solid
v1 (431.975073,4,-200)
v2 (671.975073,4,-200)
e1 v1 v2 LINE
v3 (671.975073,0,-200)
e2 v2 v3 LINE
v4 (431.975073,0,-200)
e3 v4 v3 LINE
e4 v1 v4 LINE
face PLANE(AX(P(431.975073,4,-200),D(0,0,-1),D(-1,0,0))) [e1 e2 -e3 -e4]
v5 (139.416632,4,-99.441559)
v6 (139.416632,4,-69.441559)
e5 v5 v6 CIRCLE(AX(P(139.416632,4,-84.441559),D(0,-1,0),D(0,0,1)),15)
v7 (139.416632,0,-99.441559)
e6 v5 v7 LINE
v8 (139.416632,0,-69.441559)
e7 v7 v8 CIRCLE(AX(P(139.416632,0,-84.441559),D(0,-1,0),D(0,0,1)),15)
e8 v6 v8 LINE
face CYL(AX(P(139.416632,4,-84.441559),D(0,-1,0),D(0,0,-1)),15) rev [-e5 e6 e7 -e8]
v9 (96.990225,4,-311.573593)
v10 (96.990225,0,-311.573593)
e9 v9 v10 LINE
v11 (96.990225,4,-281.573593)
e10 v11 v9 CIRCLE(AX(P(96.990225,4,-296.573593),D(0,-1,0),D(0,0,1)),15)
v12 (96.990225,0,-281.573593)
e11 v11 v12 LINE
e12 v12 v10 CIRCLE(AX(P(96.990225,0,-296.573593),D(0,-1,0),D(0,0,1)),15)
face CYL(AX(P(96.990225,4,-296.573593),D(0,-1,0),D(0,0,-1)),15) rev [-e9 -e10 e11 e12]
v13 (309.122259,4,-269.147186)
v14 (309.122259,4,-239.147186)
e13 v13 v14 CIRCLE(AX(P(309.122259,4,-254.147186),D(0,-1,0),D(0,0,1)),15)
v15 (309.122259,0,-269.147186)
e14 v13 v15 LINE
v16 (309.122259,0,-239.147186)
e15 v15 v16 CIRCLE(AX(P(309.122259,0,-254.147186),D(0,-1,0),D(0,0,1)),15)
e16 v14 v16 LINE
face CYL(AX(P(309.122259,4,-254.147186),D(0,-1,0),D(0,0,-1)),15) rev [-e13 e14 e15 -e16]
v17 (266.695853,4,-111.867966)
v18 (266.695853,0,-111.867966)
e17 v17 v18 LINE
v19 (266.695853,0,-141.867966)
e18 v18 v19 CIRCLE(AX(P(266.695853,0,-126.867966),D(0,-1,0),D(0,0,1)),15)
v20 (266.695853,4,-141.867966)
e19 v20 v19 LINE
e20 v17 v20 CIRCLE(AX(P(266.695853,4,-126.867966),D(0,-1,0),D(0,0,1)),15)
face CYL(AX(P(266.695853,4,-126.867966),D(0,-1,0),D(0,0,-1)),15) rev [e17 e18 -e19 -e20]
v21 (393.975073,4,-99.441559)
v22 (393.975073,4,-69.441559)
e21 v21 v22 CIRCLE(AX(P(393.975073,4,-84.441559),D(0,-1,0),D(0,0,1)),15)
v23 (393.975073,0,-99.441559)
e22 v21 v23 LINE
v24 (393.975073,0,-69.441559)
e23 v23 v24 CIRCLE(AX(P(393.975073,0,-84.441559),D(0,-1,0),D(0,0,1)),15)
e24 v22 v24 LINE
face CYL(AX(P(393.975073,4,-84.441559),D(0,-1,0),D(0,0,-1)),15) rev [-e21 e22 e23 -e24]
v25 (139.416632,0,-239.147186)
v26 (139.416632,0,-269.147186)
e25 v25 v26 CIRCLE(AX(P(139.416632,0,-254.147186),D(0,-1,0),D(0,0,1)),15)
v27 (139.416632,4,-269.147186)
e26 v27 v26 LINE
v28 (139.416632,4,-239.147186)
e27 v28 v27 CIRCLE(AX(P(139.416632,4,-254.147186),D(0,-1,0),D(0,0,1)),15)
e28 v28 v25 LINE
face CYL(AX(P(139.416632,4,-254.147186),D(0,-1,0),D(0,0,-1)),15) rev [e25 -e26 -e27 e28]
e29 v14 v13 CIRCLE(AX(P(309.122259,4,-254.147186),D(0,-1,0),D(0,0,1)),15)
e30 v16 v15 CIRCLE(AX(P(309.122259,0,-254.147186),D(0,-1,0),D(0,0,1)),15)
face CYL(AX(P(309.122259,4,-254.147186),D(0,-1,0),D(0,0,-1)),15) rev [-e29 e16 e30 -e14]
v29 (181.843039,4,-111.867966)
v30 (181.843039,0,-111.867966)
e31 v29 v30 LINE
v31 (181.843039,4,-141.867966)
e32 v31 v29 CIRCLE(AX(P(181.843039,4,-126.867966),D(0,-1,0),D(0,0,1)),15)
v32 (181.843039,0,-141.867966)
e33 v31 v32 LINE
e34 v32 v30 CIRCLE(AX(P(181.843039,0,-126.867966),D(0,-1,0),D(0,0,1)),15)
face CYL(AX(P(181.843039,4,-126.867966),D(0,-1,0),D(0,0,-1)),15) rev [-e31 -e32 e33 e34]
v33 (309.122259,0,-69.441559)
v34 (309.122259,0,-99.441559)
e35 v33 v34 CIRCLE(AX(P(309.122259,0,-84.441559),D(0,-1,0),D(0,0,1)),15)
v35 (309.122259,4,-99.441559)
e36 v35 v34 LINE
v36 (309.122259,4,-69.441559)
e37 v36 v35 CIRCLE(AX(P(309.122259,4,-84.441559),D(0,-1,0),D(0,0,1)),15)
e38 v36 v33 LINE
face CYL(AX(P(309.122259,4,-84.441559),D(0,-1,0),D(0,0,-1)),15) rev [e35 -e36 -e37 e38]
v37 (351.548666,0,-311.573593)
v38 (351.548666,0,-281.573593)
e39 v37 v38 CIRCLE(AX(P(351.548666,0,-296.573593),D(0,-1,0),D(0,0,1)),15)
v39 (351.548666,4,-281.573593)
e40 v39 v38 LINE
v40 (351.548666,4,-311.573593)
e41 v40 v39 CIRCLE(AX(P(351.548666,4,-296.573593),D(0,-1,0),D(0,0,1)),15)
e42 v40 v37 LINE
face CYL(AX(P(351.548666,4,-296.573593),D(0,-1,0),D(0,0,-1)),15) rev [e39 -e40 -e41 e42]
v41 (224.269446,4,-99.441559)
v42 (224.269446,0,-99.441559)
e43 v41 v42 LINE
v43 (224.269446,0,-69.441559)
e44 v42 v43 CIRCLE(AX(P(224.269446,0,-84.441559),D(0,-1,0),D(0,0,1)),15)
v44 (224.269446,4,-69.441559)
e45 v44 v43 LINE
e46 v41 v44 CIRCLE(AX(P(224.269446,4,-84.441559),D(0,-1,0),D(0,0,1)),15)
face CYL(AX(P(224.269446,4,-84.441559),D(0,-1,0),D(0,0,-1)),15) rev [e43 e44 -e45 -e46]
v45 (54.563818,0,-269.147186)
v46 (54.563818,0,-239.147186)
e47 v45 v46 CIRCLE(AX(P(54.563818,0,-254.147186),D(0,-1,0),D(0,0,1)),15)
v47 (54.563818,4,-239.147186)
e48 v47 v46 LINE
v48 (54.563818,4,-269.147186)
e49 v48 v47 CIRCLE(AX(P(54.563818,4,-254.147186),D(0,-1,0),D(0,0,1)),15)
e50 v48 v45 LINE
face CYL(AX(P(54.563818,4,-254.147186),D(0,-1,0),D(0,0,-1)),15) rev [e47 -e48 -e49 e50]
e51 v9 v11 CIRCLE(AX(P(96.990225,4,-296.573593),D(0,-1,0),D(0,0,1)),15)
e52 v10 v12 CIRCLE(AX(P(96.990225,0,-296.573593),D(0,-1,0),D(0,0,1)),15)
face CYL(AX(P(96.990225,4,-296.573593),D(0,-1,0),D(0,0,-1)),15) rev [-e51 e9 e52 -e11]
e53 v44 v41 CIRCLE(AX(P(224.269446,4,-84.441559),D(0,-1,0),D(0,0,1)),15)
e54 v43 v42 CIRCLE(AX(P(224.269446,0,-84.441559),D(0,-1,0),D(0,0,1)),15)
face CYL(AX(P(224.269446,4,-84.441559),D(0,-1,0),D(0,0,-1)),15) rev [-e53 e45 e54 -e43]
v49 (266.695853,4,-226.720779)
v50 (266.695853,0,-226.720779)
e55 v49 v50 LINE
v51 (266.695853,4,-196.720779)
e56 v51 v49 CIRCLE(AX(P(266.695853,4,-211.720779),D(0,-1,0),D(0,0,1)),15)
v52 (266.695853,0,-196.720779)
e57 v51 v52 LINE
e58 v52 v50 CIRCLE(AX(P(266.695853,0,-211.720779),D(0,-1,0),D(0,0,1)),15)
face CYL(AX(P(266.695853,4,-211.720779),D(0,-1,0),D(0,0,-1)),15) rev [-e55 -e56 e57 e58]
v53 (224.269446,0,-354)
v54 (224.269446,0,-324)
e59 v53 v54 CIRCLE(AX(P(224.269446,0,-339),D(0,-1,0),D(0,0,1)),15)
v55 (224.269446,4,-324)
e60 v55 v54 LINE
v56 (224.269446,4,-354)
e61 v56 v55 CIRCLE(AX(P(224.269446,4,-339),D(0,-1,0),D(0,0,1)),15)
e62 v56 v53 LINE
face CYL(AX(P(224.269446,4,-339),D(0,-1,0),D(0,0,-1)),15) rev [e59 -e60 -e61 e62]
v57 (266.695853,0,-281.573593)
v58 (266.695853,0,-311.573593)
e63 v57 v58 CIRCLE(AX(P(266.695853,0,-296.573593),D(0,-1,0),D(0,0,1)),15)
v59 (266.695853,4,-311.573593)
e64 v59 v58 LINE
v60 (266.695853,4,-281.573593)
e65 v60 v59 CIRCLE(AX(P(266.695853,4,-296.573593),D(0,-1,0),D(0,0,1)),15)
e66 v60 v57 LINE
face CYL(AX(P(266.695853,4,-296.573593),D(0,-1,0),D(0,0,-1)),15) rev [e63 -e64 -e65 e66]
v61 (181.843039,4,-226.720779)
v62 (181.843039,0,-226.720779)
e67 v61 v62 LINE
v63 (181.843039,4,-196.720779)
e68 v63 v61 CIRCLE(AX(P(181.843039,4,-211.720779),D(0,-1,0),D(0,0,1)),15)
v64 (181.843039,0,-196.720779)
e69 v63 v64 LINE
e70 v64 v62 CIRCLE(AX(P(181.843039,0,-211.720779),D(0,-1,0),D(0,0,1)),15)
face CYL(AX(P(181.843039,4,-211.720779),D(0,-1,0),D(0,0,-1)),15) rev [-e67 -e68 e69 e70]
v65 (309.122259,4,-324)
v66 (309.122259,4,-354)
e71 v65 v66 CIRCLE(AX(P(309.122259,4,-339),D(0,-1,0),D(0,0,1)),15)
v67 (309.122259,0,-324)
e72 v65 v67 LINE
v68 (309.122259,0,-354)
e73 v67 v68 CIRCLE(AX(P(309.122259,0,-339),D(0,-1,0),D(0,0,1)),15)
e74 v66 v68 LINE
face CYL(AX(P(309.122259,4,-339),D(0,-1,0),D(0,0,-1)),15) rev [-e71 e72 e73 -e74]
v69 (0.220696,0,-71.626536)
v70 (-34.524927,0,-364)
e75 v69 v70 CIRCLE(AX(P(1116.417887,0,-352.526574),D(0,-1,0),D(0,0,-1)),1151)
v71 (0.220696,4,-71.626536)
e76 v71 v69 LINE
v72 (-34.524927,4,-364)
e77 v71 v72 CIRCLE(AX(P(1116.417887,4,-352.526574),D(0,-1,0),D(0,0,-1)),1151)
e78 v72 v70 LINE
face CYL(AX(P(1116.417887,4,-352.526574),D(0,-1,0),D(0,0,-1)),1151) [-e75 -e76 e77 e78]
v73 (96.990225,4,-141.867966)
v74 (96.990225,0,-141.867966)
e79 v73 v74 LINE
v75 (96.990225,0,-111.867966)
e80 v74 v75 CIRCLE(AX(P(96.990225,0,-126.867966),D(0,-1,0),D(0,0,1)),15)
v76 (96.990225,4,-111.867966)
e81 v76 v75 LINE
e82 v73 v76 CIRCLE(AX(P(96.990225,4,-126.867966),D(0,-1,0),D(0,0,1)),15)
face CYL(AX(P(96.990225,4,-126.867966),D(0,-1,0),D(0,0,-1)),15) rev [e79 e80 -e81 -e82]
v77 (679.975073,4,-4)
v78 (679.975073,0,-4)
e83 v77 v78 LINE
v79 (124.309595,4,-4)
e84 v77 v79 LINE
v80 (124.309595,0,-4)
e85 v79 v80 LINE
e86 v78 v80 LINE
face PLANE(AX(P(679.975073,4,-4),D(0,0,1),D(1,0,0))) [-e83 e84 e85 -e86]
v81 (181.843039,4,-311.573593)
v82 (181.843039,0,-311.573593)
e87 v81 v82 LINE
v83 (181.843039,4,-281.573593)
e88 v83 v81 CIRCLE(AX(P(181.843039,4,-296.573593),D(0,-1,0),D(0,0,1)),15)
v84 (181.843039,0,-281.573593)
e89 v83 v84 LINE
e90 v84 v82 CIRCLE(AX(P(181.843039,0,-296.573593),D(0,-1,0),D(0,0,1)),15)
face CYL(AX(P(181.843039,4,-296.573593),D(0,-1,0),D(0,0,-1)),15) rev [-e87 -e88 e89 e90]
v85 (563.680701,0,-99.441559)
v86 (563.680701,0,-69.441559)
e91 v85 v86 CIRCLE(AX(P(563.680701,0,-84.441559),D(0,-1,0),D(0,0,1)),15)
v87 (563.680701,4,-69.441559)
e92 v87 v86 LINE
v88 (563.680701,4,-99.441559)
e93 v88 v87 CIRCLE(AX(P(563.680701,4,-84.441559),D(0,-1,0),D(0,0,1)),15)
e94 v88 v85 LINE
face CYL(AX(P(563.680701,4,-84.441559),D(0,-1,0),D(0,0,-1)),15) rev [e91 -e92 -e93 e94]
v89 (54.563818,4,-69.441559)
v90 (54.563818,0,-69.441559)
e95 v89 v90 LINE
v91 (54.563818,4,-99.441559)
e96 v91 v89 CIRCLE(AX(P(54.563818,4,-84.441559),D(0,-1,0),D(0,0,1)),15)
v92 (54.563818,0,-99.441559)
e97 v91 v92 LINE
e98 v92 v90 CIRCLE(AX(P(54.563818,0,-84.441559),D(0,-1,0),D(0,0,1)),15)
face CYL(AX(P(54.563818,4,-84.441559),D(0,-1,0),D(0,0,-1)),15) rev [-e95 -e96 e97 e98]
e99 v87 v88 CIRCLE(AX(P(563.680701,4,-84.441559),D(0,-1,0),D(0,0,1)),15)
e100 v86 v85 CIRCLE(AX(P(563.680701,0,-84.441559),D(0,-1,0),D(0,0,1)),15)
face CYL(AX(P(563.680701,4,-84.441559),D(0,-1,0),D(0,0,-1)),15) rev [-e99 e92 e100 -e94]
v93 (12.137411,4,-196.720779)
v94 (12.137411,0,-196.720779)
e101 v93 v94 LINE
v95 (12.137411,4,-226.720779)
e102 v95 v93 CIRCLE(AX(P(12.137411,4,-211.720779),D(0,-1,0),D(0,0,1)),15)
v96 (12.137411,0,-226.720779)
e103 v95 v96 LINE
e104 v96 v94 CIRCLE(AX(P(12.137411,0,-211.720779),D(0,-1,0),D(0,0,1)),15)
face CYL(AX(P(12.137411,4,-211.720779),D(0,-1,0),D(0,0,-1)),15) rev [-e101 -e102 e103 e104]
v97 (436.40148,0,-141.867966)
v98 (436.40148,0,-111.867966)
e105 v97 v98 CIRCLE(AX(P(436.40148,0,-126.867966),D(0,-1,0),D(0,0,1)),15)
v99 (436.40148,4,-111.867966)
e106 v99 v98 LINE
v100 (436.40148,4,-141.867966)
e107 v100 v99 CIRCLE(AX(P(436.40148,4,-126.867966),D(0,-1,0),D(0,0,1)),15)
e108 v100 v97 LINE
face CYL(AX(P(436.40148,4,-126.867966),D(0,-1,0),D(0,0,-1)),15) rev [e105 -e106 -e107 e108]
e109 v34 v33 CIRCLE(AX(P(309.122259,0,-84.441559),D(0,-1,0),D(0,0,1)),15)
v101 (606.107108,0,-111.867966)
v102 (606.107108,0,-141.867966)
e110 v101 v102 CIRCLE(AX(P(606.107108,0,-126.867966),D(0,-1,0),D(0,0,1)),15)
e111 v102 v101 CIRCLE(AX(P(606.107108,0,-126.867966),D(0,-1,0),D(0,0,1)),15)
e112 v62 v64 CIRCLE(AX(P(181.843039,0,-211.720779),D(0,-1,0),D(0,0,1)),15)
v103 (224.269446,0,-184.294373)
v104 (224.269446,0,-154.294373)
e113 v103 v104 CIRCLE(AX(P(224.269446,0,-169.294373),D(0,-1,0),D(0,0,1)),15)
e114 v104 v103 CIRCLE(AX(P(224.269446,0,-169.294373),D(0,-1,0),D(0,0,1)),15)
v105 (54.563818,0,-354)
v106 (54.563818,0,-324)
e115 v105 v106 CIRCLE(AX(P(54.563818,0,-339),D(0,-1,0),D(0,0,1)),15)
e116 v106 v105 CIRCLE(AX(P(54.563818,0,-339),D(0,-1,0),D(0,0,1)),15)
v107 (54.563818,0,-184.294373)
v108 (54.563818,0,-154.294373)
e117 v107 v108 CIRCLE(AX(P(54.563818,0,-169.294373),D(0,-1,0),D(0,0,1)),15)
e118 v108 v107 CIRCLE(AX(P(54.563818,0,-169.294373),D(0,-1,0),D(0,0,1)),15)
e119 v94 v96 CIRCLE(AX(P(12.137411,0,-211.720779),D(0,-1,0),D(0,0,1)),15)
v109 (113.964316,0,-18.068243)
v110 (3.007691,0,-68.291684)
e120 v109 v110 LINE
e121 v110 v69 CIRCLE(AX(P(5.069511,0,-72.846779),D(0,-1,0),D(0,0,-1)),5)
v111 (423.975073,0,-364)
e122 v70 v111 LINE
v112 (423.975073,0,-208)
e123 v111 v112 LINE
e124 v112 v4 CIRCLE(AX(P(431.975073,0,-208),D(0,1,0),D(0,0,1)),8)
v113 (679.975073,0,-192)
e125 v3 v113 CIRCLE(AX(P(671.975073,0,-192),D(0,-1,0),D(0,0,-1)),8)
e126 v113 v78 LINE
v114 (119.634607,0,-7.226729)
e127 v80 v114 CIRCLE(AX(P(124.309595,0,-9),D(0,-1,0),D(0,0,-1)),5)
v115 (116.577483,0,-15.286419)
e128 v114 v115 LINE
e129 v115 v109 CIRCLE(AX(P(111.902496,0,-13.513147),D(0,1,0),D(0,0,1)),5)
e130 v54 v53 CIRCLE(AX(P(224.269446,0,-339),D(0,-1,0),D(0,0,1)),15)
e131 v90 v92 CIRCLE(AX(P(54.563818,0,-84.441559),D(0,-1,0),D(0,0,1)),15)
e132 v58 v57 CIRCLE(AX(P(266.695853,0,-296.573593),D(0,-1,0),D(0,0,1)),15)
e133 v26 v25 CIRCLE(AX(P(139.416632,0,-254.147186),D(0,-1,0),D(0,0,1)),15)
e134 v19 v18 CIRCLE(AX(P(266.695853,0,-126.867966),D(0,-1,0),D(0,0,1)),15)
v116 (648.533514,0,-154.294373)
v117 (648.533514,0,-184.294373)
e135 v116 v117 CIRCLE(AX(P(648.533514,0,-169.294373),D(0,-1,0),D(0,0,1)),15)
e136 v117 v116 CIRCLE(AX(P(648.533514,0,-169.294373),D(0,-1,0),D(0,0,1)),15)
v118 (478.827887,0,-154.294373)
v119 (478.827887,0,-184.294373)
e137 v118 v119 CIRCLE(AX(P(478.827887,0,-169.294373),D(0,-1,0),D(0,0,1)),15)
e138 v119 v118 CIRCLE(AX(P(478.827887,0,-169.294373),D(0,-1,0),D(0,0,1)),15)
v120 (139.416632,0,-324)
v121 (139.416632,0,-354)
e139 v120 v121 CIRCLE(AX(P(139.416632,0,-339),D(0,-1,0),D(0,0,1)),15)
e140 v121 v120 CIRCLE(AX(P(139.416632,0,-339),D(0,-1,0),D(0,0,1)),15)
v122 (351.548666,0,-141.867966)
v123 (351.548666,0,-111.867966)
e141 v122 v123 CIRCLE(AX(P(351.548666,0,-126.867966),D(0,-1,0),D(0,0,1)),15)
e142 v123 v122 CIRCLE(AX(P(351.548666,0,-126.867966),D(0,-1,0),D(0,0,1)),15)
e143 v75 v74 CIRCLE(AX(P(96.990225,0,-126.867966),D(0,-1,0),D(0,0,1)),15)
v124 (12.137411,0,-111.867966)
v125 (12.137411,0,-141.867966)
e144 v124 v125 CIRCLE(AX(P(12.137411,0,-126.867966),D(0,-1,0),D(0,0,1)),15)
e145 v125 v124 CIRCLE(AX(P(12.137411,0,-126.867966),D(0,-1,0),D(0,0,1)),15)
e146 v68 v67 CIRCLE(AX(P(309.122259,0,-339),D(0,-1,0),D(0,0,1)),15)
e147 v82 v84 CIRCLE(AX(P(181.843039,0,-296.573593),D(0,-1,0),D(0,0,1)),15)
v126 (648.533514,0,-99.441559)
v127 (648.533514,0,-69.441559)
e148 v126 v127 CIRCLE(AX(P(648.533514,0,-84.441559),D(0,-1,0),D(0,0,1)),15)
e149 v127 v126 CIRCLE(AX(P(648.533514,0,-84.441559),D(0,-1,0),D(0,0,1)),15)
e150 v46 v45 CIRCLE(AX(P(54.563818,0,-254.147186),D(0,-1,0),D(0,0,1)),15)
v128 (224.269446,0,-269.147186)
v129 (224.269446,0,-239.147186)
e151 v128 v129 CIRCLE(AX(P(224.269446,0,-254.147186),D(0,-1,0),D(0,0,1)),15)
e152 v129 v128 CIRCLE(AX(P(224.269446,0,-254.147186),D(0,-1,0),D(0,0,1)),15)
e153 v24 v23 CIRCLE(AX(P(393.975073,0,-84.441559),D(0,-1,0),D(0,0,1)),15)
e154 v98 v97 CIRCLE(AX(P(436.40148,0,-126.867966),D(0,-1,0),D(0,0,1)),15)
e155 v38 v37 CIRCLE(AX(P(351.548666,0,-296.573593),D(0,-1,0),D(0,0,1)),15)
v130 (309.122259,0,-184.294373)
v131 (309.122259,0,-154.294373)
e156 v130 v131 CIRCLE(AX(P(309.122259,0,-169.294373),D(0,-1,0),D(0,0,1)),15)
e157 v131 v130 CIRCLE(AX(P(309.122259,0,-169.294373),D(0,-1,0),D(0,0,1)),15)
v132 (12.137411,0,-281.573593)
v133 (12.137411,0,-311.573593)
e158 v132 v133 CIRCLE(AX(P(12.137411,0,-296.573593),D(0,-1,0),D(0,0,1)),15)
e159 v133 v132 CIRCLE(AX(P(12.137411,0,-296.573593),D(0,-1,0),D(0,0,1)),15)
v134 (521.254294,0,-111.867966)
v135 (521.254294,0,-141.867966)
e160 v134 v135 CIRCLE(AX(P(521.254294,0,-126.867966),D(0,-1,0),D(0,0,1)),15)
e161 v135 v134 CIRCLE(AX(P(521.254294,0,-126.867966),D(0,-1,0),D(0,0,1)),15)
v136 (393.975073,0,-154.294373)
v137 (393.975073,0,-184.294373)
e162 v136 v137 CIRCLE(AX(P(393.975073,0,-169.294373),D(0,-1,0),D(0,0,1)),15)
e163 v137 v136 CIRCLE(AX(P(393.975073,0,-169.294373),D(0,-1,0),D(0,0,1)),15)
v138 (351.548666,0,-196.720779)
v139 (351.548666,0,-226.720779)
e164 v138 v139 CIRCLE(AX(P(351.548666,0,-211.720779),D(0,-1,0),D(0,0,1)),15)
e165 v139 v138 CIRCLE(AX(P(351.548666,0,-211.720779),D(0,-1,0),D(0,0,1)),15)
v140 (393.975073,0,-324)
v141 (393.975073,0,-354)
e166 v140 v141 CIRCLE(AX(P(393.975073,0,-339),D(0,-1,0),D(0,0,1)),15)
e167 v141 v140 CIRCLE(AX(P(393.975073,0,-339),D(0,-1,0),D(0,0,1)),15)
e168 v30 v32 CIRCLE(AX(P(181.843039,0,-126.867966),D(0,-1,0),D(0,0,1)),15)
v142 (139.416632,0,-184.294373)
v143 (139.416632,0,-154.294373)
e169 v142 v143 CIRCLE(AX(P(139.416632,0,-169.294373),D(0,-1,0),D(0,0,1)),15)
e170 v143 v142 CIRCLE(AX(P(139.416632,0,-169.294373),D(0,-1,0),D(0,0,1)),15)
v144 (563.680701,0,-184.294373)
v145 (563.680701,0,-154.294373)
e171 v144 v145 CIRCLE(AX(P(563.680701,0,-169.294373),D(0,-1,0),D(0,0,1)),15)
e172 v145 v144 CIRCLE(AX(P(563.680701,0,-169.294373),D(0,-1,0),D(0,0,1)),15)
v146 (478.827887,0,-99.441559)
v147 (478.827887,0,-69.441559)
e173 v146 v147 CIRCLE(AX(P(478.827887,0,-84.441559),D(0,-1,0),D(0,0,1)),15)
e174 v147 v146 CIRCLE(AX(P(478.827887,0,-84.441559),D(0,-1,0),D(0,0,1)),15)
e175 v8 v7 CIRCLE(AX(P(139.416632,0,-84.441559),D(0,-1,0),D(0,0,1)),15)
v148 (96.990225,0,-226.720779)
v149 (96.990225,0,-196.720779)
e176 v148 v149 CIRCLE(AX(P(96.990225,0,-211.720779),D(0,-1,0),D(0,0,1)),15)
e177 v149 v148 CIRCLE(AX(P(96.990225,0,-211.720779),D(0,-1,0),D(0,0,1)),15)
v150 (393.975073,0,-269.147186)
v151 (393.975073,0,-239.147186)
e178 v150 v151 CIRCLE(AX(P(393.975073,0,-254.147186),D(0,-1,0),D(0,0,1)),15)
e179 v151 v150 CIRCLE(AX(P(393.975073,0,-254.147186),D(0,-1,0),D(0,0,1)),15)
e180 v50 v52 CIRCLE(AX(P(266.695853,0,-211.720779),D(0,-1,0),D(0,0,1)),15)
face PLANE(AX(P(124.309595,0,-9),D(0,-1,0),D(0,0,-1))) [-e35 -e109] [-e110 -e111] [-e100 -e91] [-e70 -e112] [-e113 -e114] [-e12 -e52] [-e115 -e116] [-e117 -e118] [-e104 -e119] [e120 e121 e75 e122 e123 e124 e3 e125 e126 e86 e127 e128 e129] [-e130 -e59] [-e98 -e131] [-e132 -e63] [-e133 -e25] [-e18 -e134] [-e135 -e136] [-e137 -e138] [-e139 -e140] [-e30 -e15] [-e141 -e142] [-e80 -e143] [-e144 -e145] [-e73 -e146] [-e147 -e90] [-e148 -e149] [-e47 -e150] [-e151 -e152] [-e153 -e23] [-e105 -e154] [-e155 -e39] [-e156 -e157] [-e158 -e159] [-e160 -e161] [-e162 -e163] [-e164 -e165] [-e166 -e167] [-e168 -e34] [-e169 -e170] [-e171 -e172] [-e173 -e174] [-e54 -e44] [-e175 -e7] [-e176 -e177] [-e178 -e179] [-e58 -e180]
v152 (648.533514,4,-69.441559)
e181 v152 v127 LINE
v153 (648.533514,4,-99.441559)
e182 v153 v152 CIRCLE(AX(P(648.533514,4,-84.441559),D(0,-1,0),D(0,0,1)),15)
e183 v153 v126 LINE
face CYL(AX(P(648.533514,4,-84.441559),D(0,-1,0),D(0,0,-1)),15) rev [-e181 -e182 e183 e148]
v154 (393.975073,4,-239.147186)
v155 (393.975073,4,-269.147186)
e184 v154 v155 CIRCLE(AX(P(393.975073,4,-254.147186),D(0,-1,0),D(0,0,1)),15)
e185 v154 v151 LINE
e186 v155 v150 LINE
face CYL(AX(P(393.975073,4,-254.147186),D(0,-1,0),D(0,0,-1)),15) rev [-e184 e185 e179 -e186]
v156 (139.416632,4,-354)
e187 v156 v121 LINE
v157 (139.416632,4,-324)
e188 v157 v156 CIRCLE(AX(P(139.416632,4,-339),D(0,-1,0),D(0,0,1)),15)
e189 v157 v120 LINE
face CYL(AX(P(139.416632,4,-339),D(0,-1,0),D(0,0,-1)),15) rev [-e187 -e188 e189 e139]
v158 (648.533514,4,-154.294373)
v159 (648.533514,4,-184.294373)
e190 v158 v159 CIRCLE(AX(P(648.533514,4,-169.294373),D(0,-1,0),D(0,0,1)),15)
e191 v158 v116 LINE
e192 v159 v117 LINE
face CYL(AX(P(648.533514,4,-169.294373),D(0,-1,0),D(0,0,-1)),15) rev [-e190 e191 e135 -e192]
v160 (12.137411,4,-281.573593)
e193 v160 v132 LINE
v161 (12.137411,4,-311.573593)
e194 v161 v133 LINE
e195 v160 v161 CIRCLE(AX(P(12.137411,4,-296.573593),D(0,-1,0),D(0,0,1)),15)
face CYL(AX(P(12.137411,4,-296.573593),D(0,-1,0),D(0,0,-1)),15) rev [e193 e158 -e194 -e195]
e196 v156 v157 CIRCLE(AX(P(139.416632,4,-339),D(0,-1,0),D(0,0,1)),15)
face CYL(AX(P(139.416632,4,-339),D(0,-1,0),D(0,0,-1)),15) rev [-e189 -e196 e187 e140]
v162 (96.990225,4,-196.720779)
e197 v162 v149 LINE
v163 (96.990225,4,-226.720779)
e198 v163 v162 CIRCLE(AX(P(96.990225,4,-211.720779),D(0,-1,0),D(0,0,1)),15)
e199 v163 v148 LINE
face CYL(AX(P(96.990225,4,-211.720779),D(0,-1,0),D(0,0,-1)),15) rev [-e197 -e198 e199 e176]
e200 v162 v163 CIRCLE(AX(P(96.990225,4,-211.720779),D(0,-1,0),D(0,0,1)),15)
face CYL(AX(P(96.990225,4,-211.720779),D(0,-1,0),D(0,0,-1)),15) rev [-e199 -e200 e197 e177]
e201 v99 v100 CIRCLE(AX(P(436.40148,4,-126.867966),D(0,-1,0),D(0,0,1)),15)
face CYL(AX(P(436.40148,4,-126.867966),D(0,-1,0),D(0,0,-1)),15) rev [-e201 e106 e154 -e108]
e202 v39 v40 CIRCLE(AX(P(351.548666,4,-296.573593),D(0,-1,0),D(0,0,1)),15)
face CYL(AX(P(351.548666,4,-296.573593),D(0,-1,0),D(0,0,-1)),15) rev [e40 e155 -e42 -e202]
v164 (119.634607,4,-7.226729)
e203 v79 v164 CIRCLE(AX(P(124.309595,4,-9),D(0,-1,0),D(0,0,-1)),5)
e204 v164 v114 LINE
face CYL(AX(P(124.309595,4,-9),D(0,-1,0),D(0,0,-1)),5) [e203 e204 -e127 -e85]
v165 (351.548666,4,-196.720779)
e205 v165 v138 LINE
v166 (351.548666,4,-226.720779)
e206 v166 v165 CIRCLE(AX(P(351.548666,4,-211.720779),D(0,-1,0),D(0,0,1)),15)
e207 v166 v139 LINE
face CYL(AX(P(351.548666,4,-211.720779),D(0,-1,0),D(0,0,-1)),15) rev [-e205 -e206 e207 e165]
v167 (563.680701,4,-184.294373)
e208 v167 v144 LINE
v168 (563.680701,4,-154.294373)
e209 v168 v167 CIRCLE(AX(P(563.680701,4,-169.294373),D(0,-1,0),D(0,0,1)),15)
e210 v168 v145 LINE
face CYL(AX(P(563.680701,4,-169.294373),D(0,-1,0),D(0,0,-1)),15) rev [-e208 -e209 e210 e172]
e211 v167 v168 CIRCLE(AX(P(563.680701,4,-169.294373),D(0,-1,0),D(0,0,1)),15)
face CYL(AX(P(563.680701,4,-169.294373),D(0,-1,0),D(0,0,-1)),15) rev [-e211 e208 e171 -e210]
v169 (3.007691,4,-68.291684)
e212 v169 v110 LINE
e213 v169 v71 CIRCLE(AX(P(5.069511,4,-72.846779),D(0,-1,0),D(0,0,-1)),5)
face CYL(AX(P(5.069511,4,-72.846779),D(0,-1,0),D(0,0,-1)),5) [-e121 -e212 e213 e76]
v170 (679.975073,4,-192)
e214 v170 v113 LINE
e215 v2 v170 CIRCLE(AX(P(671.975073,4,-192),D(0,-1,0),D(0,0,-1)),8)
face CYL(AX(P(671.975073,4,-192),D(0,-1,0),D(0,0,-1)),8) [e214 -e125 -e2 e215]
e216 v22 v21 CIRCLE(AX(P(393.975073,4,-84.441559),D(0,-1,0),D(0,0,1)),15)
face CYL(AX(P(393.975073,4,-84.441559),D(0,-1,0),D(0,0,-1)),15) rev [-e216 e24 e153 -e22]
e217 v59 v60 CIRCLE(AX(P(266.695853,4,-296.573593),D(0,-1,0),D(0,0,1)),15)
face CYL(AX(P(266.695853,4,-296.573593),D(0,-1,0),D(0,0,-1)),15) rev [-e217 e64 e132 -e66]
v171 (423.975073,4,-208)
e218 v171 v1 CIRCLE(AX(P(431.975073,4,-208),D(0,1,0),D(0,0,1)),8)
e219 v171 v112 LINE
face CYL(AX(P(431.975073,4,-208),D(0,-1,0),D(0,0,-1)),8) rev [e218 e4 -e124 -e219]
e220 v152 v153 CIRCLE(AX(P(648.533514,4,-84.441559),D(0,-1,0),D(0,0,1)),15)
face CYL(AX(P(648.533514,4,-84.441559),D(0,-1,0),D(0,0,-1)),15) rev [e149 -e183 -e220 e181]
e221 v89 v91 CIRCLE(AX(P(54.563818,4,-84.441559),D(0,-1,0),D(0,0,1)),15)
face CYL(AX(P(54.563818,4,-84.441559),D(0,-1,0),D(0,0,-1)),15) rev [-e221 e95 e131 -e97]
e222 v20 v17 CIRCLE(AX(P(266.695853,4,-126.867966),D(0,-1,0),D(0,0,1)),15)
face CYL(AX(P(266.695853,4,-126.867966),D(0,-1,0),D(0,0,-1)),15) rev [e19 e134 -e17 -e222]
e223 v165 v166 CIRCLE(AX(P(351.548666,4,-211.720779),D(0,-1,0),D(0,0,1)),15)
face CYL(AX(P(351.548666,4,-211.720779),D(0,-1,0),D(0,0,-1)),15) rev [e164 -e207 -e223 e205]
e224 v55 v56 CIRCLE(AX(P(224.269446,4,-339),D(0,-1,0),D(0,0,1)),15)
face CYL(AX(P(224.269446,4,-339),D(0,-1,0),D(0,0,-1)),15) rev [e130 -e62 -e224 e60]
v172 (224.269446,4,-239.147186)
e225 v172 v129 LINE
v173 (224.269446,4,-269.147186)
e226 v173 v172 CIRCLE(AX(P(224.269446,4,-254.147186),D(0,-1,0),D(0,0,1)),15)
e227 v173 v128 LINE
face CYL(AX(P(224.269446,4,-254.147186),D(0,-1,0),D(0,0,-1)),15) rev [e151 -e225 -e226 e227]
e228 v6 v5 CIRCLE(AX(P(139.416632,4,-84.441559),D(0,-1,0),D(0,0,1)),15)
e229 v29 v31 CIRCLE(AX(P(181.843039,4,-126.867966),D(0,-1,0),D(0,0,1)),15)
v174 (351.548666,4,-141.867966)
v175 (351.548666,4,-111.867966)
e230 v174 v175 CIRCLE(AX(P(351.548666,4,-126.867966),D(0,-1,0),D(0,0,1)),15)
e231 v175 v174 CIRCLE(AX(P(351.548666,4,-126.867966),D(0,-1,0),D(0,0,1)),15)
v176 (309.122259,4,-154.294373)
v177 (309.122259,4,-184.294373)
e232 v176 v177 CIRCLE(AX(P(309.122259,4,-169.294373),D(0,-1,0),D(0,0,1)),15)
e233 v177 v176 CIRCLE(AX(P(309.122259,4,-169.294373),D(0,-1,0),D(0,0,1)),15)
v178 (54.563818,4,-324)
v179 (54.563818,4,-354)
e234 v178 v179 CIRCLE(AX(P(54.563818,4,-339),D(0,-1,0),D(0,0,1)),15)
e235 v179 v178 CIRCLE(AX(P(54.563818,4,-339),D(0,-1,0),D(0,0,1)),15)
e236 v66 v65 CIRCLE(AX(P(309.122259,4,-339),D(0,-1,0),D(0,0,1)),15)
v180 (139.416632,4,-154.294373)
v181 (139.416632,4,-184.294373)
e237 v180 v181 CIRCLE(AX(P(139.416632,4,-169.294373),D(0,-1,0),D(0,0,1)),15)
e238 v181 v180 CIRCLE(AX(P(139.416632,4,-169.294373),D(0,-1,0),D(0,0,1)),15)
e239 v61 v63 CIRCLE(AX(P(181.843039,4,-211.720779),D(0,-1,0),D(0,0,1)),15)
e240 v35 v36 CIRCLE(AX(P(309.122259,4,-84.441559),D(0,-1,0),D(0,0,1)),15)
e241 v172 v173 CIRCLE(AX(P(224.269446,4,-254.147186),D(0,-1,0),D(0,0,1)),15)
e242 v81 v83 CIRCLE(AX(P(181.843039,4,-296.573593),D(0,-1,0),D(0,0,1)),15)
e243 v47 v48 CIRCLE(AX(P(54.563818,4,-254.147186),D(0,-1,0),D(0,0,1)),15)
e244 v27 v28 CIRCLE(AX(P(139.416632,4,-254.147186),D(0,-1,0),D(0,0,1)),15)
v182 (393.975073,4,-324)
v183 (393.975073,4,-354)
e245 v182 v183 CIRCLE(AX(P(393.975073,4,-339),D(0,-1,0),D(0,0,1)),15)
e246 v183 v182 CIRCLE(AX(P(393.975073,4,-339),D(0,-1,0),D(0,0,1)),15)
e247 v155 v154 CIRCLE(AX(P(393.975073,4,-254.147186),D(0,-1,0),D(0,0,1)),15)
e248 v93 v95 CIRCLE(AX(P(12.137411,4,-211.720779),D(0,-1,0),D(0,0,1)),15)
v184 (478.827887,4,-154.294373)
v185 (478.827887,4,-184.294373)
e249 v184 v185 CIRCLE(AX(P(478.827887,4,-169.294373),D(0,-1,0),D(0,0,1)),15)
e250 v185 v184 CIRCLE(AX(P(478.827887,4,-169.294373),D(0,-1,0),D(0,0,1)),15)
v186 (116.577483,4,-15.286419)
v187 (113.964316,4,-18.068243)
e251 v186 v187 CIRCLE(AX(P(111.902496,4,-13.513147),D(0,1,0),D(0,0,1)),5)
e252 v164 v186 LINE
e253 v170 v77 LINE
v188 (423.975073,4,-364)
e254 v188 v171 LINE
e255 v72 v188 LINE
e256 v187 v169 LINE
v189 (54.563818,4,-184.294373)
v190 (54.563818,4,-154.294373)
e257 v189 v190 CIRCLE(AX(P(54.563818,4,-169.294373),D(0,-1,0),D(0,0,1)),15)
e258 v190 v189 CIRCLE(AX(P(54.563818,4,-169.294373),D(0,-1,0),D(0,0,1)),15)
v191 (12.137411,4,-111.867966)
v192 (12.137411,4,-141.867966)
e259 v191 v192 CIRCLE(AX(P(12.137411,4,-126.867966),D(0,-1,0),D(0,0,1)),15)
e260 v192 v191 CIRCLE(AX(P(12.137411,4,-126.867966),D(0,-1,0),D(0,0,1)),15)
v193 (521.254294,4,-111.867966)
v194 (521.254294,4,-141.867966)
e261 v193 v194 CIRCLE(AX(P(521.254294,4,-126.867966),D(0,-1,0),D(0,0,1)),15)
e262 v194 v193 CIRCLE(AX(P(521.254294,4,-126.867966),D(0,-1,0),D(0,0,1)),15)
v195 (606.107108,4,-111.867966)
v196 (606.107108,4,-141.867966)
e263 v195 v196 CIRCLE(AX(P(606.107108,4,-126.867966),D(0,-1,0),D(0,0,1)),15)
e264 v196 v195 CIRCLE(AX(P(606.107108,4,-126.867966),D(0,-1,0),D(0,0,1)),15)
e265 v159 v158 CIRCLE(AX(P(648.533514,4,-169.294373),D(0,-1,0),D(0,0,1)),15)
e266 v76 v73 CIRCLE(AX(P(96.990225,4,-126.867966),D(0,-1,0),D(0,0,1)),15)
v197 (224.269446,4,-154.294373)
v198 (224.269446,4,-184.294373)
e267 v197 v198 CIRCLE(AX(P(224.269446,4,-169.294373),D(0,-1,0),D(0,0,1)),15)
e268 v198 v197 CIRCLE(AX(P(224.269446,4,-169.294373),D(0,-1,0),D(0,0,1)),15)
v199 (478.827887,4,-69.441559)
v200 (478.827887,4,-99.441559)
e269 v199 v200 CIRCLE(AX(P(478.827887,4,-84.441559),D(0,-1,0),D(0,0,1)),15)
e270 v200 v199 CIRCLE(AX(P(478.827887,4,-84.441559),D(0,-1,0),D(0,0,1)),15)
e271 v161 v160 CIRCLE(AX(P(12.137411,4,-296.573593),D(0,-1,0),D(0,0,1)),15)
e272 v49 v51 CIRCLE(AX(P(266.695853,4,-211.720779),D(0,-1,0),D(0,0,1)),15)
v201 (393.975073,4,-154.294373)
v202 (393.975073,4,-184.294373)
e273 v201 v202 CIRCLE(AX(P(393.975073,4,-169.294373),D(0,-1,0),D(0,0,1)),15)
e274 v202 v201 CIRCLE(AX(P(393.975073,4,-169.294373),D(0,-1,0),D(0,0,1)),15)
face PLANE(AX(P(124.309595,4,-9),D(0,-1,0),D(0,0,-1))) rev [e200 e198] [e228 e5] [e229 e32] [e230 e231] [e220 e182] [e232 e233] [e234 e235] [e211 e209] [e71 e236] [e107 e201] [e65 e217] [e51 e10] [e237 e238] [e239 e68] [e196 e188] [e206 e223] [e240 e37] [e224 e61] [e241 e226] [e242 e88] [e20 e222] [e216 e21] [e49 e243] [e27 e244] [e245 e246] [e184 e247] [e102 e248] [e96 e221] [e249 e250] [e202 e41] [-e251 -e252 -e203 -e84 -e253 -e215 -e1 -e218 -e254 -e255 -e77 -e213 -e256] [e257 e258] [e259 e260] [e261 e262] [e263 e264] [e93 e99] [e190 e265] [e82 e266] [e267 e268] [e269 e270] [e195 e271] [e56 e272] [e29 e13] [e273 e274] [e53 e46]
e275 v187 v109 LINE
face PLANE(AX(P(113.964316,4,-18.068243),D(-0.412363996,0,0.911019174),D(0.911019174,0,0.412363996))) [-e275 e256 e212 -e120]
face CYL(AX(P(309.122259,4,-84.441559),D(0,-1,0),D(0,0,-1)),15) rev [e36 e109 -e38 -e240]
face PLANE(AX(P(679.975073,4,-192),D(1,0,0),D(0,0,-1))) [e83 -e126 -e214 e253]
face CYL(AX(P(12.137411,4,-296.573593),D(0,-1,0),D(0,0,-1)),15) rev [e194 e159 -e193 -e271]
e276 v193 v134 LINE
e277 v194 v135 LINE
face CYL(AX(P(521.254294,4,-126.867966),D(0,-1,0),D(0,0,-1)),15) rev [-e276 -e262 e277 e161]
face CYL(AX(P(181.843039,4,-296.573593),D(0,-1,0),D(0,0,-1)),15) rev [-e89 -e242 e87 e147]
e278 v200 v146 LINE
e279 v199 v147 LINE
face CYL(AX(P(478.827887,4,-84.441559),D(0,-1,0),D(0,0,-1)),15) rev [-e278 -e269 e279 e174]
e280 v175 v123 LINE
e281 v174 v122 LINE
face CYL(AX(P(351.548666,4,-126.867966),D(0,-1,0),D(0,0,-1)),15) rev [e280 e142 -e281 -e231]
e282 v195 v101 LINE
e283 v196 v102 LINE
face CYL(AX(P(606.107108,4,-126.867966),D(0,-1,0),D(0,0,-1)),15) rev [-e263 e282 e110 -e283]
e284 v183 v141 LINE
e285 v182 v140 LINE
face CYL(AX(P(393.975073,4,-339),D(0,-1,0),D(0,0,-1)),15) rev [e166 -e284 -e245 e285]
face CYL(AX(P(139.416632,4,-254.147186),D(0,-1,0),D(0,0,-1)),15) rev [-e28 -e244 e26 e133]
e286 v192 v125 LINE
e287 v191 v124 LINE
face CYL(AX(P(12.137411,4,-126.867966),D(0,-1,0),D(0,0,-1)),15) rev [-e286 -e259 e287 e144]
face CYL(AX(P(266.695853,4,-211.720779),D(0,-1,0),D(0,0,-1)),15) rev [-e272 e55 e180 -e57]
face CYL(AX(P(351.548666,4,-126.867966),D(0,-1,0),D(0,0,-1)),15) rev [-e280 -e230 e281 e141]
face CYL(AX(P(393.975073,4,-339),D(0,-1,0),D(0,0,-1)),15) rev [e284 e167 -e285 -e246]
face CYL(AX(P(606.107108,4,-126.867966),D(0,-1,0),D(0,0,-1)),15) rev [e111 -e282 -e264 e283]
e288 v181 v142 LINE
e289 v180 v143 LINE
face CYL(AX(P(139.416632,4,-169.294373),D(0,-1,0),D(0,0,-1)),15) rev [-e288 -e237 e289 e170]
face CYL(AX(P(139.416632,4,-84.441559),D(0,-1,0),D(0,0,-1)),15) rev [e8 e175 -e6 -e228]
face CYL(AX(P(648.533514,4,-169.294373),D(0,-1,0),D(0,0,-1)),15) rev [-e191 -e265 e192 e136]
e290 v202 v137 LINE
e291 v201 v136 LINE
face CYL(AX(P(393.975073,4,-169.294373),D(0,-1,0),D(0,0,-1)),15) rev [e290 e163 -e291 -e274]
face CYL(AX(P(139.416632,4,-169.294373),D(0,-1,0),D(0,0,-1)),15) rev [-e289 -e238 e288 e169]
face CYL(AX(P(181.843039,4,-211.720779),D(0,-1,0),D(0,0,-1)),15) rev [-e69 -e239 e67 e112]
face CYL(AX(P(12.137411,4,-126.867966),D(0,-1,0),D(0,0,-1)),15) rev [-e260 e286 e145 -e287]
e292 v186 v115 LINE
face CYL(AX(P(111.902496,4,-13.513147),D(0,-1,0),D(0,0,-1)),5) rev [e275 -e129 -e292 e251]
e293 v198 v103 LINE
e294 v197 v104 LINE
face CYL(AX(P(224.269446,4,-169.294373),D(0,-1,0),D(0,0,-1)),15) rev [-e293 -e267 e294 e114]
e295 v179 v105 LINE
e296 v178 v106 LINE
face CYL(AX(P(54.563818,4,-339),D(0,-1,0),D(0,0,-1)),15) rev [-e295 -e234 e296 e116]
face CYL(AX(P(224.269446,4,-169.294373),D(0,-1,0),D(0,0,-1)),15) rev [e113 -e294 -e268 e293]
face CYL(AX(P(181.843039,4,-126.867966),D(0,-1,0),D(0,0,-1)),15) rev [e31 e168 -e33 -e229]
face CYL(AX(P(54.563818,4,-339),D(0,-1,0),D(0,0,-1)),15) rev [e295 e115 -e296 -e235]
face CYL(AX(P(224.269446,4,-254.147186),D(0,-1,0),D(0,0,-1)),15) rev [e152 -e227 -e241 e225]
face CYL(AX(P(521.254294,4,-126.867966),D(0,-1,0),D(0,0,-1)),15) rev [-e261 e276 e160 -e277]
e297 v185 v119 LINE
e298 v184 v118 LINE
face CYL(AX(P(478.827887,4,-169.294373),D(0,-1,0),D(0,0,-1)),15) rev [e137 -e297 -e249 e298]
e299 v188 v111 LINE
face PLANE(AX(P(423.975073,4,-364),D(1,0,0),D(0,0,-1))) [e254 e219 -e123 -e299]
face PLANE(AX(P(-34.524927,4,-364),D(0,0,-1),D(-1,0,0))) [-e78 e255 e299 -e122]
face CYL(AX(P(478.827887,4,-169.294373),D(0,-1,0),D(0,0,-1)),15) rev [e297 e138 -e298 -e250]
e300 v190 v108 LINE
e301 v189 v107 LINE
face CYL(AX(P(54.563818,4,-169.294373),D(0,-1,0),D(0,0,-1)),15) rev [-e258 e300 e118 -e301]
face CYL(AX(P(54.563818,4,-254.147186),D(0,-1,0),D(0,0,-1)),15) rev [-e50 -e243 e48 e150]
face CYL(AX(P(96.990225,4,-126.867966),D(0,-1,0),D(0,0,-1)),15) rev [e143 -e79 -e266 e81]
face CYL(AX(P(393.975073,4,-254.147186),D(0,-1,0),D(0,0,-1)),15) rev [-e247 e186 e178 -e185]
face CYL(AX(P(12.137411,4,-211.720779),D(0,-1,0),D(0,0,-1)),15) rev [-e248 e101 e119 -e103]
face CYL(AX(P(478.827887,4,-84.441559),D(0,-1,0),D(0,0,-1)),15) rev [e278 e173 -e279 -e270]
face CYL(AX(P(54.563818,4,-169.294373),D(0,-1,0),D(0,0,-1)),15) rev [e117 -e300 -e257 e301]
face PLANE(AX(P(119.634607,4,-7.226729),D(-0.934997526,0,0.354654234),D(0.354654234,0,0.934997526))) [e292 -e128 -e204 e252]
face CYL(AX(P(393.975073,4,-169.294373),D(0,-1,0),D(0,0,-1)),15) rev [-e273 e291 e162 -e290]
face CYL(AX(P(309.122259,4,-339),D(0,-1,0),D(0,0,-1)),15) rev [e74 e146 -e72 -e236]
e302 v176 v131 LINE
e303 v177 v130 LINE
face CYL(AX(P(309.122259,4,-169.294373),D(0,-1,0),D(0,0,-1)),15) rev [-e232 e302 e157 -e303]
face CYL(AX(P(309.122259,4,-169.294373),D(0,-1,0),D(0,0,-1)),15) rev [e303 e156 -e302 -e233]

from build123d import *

# Parameters (mm, degrees)
SKETCH1_R           = 15
BOSS_EXTRUDE1_DEPTH = 4


with BuildPart() as part:
    # Sketch1 → Boss-Extrude1 (new body)
    with BuildSketch(Plane.XZ):
        with BuildLine():
            Line((119.63460713, -7.226728829), (116.577483445, -15.286418544))
            ThreePointArc((116.577483445, -15.286418544), (115.546776451, -16.936481806), (113.964315794, -18.068243242))
            Line((113.964315794, -18.068243242), (3.00769119, -68.291683558))
            ThreePointArc((3.00769119, -68.291683558), (1.232907358, -69.640462039), (0.220696267, -71.626535993))
            ThreePointArc((0.220696267, -71.626535993), (-26.539465951, -216.697676507), (-34.524926809, -364))
            Line((-34.524926809, -364), (423.975073191, -364))
            Line((423.975073191, -364), (423.975073191, -208))
            ThreePointArc((423.975073191, -208), (426.318218942, -202.343145751), (431.975073191, -200))
            Line((431.975073191, -200), (671.975073191, -200))
            ThreePointArc((671.975073191, -200), (677.63192744, -197.656854249), (679.975073191, -192))
            Line((679.975073191, -192), (679.975073191, -4))
            Line((679.975073191, -4), (124.309594762, -4))
            ThreePointArc((124.309594762, -4), (121.469379616, -4.885005719), (119.63460713, -7.226728829))
        make_face()
        with Locations(Location((393.975073191, -254.147186258, 0), (0, 0, 90))):
            Circle(SKETCH1_R, mode=Mode.SUBTRACT)
        with Locations(Location((351.54866632, -296.573593129, 0), (0, 0, 90))):
            Circle(SKETCH1_R, mode=Mode.SUBTRACT)
        with Locations(Location((309.122259449, -339, 0), (0, 0, 90))):
            Circle(SKETCH1_R, mode=Mode.SUBTRACT)
        with Locations(Location((393.975073191, -169.294372515, 0), (0, 0, 90))):
            Circle(SKETCH1_R, mode=Mode.SUBTRACT)
        with Locations(Location((351.54866632, -211.720779386, 0), (0, 0, 90))):
            Circle(SKETCH1_R, mode=Mode.SUBTRACT)
        with Locations(Location((309.122259449, -254.147186258, 0), (0, 0, 90))):
            Circle(SKETCH1_R, mode=Mode.SUBTRACT)
        with Locations(Location((266.695852577, -296.573593129, 0), (0, 0, 90))):
            Circle(SKETCH1_R, mode=Mode.SUBTRACT)
        with Locations(Location((224.269445706, -339, 0), (0, 0, 90))):
            Circle(SKETCH1_R, mode=Mode.SUBTRACT)
        with Locations(Location((478.827886933, -169.294372515, 0), (0, 0, 90))):
            Circle(SKETCH1_R, mode=Mode.SUBTRACT)
        with Locations(Location((436.401480062, -126.867965644, 0), (0, 0, 90))):
            Circle(SKETCH1_R, mode=Mode.SUBTRACT)
        with Locations(Location((393.975073191, -84.441558773, 0), (0, 0, 90))):
            Circle(SKETCH1_R, mode=Mode.SUBTRACT)
        with Locations(Location((351.54866632, -126.867965644, 0), (0, 0, 90))):
            Circle(SKETCH1_R, mode=Mode.SUBTRACT)
        with Locations(Location((309.122259449, -169.294372515, 0), (0, 0, 90))):
            Circle(SKETCH1_R, mode=Mode.SUBTRACT)
        with Locations(Location((266.695852577, -211.720779386, 0), (0, 0, 90))):
            Circle(SKETCH1_R, mode=Mode.SUBTRACT)
        with Locations(Location((224.269445706, -254.147186258, 0), (0, 0, 90))):
            Circle(SKETCH1_R, mode=Mode.SUBTRACT)
        with Locations(Location((181.843038835, -296.573593129, 0), (0, 0, 90))):
            Circle(SKETCH1_R, mode=Mode.SUBTRACT)
        with Locations(Location((139.416631964, -339, 0), (0, 0, 90))):
            Circle(SKETCH1_R, mode=Mode.SUBTRACT)
        with Locations(Location((563.680700676, -169.294372515, 0), (0, 0, 90))):
            Circle(SKETCH1_R, mode=Mode.SUBTRACT)
        with Locations(Location((521.254293805, -126.867965644, 0), (0, 0, 90))):
            Circle(SKETCH1_R, mode=Mode.SUBTRACT)
        with Locations(Location((478.827886933, -84.441558773, 0), (0, 0, 90))):
            Circle(SKETCH1_R, mode=Mode.SUBTRACT)
        with Locations(Location((309.122259449, -84.441558773, 0), (0, 0, 90))):
            Circle(SKETCH1_R, mode=Mode.SUBTRACT)
        with Locations(Location((266.695852577, -126.867965644, 0), (0, 0, 90))):
            Circle(SKETCH1_R, mode=Mode.SUBTRACT)
        with Locations(Location((224.269445706, -169.294372515, 0), (0, 0, 90))):
            Circle(SKETCH1_R, mode=Mode.SUBTRACT)
        with Locations(Location((181.843038835, -211.720779386, 0), (0, 0, 90))):
            Circle(SKETCH1_R, mode=Mode.SUBTRACT)
        with Locations(Location((139.416631964, -254.147186258, 0), (0, 0, 90))):
            Circle(SKETCH1_R, mode=Mode.SUBTRACT)
        with Locations(Location((96.990225093, -296.573593129, 0), (0, 0, 90))):
            Circle(SKETCH1_R, mode=Mode.SUBTRACT)
        with Locations(Location((54.563818221, -339, 0), (0, 0, 90))):
            Circle(SKETCH1_R, mode=Mode.SUBTRACT)
        with Locations(Location((648.533514418, -169.294372515, 0), (0, 0, 90))):
            Circle(SKETCH1_R, mode=Mode.SUBTRACT)
        with Locations(Location((606.107107547, -126.867965644, 0), (0, 0, 90))):
            Circle(SKETCH1_R, mode=Mode.SUBTRACT)
        with Locations(Location((563.680700676, -84.441558773, 0), (0, 0, 90))):
            Circle(SKETCH1_R, mode=Mode.SUBTRACT)
        with Locations(Location((224.269445706, -84.441558773, 0), (0, 0, 90))):
            Circle(SKETCH1_R, mode=Mode.SUBTRACT)
        with Locations(Location((181.843038835, -126.867965644, 0), (0, 0, 90))):
            Circle(SKETCH1_R, mode=Mode.SUBTRACT)
        with Locations(Location((139.416631964, -169.294372515, 0), (0, 0, 90))):
            Circle(SKETCH1_R, mode=Mode.SUBTRACT)
        with Locations(Location((96.990225093, -211.720779386, 0), (0, 0, 90))):
            Circle(SKETCH1_R, mode=Mode.SUBTRACT)
        with Locations(Location((54.563818221, -254.147186258, 0), (0, 0, 90))):
            Circle(SKETCH1_R, mode=Mode.SUBTRACT)
        with Locations(Location((12.13741135, -296.573593129, 0), (0, 0, 90))):
            Circle(SKETCH1_R, mode=Mode.SUBTRACT)
        with Locations(Location((648.533514418, -84.441558773, 0), (0, 0, 90))):
            Circle(SKETCH1_R, mode=Mode.SUBTRACT)
        with Locations(Location((139.416631964, -84.441558773, 0), (0, 0, 90))):
            Circle(SKETCH1_R, mode=Mode.SUBTRACT)
        with Locations(Location((96.990225093, -126.867965644, 0), (0, 0, 90))):
            Circle(SKETCH1_R, mode=Mode.SUBTRACT)
        with Locations(Location((54.563818221, -169.294372515, 0), (0, 0, 90))):
            Circle(SKETCH1_R, mode=Mode.SUBTRACT)
        with Locations(Location((12.13741135, -211.720779386, 0), (0, 0, 90))):
            Circle(SKETCH1_R, mode=Mode.SUBTRACT)
        with Locations(Location((54.563818221, -84.441558773, 0), (0, 0, 90))):
            Circle(SKETCH1_R, mode=Mode.SUBTRACT)
        with Locations(Location((12.13741135, -126.867965644, 0), (0, 0, 90))):
            Circle(SKETCH1_R, mode=Mode.SUBTRACT)
        with Locations(Location((393.975073191, -339, 0), (0, 0, 90))):
            Circle(SKETCH1_R, mode=Mode.SUBTRACT)
    extrude(amount=-BOSS_EXTRUDE1_DEPTH)


solid = part.part
